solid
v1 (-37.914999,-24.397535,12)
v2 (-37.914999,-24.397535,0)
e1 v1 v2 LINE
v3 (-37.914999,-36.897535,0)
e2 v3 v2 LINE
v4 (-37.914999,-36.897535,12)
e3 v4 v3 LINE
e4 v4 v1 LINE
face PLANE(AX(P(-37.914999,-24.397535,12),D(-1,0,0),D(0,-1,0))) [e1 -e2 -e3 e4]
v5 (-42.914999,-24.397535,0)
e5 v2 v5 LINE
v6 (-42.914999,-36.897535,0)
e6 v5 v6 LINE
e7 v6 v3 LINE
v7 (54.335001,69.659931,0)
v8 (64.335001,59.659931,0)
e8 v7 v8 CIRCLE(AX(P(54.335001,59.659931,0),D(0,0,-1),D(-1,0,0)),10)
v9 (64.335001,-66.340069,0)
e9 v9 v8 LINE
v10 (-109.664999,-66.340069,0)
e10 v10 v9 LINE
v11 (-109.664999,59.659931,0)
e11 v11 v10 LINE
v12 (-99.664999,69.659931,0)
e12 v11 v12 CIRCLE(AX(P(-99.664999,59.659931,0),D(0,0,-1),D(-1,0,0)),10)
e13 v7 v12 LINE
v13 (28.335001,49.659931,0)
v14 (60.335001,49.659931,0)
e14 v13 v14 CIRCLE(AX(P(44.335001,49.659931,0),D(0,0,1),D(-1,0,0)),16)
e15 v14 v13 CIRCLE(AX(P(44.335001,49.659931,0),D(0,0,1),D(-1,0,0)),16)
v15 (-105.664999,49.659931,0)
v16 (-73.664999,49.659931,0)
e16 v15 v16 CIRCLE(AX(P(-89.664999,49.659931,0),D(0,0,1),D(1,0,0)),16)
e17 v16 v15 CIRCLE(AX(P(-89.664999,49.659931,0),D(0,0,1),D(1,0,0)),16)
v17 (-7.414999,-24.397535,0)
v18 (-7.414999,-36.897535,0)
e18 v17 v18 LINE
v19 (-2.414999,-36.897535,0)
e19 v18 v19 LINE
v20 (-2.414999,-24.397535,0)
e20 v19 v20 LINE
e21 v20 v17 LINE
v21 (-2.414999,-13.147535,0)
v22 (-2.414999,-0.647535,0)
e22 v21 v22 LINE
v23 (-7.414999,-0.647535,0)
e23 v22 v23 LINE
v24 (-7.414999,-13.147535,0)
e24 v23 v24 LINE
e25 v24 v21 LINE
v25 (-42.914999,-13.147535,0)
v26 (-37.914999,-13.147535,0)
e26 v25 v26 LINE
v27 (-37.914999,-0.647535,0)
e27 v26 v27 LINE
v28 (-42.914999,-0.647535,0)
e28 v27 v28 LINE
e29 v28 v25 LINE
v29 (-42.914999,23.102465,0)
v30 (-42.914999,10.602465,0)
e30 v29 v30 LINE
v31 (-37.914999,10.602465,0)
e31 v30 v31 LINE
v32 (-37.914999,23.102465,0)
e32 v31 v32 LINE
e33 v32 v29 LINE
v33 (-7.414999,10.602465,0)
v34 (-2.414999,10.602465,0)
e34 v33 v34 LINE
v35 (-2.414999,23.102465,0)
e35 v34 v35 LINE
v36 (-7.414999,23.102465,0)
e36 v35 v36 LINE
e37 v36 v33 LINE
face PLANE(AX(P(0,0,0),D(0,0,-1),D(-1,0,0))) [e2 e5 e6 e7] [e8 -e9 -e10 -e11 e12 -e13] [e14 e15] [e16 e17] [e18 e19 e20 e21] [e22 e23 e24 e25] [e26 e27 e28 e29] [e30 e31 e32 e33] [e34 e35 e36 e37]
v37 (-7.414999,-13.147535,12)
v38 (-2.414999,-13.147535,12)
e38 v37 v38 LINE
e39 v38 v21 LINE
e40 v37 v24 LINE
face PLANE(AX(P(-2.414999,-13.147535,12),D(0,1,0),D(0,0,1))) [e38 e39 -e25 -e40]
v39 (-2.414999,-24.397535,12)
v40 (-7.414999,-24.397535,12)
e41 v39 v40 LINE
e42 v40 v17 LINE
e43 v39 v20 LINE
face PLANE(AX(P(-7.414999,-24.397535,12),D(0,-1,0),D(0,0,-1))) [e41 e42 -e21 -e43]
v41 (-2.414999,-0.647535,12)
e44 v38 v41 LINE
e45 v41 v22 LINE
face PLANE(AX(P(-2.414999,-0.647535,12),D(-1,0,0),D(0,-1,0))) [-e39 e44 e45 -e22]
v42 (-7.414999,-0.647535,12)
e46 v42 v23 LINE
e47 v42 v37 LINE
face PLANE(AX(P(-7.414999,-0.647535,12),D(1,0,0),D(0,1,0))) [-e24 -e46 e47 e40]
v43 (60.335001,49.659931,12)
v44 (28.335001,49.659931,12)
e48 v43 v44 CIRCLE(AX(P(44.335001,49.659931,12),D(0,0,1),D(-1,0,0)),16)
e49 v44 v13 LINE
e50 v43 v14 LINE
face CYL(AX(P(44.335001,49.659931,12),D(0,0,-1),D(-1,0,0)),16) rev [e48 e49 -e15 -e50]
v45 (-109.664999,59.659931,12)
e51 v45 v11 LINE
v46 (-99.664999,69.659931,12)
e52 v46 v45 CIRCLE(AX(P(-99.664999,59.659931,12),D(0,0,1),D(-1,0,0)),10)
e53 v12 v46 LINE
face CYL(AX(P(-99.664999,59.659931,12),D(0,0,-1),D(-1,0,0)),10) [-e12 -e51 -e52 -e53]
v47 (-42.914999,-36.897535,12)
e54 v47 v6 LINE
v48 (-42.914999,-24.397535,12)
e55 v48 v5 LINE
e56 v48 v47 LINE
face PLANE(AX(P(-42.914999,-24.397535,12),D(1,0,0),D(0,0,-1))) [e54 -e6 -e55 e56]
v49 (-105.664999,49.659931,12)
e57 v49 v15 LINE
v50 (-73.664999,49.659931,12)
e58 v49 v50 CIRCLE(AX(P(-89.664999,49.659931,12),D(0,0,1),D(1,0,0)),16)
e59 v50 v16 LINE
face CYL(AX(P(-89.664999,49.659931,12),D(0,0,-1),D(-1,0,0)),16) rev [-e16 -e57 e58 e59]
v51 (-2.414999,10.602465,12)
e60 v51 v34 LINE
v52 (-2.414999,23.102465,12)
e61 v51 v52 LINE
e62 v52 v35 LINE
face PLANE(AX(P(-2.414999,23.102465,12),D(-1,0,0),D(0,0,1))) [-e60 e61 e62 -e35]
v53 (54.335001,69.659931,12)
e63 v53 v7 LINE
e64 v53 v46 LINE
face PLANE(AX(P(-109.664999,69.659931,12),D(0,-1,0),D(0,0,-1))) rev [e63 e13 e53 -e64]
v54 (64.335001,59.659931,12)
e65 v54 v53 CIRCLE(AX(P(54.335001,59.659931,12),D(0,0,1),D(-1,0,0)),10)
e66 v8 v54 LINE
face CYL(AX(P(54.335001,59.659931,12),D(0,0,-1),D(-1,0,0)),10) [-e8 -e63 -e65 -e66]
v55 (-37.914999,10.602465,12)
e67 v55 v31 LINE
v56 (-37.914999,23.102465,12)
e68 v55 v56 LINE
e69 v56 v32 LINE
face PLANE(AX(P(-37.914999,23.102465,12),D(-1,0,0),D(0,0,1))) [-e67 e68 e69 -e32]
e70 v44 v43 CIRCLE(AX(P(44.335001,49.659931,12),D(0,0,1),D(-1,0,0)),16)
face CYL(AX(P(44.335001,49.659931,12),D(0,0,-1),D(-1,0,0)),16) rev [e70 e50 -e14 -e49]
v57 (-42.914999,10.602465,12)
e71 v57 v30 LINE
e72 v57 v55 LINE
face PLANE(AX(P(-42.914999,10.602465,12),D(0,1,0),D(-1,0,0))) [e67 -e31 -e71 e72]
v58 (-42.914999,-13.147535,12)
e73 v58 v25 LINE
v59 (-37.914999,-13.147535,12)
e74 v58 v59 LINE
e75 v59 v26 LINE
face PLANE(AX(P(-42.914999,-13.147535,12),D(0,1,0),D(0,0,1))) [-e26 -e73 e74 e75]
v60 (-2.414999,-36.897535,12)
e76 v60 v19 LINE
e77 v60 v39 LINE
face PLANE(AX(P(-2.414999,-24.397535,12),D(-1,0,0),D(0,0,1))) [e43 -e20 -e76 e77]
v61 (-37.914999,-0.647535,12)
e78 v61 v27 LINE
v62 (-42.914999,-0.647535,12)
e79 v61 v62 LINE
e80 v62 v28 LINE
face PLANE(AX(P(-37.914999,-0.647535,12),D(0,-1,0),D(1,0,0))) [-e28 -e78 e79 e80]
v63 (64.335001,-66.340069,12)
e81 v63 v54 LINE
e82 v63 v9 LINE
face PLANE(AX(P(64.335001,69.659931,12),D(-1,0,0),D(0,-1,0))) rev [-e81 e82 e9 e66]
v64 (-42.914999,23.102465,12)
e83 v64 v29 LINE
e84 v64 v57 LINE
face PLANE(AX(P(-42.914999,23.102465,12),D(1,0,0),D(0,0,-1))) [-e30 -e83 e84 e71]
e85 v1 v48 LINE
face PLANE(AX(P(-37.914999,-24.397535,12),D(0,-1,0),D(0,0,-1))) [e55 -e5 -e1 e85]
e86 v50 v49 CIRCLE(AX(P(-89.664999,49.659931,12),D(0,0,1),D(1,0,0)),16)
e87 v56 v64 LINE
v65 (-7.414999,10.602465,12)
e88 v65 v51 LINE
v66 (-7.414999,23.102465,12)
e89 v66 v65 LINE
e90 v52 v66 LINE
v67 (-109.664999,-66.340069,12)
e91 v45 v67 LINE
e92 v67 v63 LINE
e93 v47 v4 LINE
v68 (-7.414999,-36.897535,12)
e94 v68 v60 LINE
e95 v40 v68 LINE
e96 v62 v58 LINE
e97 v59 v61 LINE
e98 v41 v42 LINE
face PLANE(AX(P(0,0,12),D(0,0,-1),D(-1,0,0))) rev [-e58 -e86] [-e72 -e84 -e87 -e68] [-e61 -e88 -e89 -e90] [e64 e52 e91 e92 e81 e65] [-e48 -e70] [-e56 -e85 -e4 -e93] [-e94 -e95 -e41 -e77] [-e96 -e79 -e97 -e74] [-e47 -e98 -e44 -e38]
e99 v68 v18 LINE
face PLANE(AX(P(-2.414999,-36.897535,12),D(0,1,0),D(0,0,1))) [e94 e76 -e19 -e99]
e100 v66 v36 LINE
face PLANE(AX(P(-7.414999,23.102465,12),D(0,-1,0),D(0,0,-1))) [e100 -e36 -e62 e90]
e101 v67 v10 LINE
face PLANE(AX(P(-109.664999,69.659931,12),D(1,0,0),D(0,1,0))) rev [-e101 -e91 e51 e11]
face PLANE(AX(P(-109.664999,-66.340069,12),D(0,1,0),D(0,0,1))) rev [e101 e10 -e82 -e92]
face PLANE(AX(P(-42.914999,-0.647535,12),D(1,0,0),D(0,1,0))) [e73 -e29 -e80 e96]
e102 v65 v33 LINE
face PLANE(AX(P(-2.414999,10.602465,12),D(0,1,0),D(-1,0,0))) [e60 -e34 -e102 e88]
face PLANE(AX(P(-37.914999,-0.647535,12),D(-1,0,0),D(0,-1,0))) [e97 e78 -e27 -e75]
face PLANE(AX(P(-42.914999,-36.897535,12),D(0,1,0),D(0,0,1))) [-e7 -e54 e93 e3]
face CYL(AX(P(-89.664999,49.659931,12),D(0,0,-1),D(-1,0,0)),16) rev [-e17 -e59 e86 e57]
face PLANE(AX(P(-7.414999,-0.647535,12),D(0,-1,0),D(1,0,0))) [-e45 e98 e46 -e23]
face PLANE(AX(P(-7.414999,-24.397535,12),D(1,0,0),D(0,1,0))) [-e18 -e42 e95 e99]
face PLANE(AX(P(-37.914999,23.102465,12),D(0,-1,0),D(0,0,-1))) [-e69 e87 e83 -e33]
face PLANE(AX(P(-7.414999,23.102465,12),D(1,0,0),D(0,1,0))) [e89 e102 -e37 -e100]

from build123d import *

# Parameters (mm, degrees)
SKETCH_1_W      = 174
SKETCH_1_H      = 136
SKETCH_1_R      = 16
SKETCH_1_W_2    = 5
SKETCH_1_H_2    = 12.5
EXTRUDE_1_DEPTH = 12
FILLET_2_R      = 10


with BuildPart() as part:
    # 草图1 → 凸台-拉伸1 (new body)
    with BuildSketch(Plane.XY):
        with Locations((-22.664999192, 1.659931171)):
            Rectangle(SKETCH_1_W, SKETCH_1_H)
        with Locations((-89.664999192, 49.659931171)):
            Circle(SKETCH_1_R, mode=Mode.SUBTRACT)
        with Locations(Location((44.335000808, 49.659931171, 0), (0, 0, 180))):
            Circle(SKETCH_1_R, mode=Mode.SUBTRACT)
        with Locations((-40.414999192, 16.852464835)):
            Rectangle(SKETCH_1_W_2, SKETCH_1_H_2, mode=Mode.SUBTRACT)
        with Locations((-40.414999192, -6.897535165)):
            Rectangle(SKETCH_1_W_2, SKETCH_1_H_2, mode=Mode.SUBTRACT)
        with Locations((-40.414999192, -30.647535165)):
            Rectangle(SKETCH_1_W_2, SKETCH_1_H_2, mode=Mode.SUBTRACT)
        with Locations((-4.914999192, -30.647535165)):
            Rectangle(SKETCH_1_W_2, SKETCH_1_H_2, mode=Mode.SUBTRACT)
        with Locations((-4.914999192, -6.897535165)):
            Rectangle(SKETCH_1_W_2, SKETCH_1_H_2, mode=Mode.SUBTRACT)
        with Locations((-4.914999192, 16.852464835)):
            Rectangle(SKETCH_1_W_2, SKETCH_1_H_2, mode=Mode.SUBTRACT)
    extrude(amount=EXTRUDE_1_DEPTH)

    # 圆角2
    fillet_2_edges = [part.edges().sort_by_distance(p)[0] for p in [
        (64.335000808, 69.659931171, 6),
        (-109.664999192, 69.659931171, 6),
    ]]
    fillet(fillet_2_edges, radius=FILLET_2_R)


solid = part.part
